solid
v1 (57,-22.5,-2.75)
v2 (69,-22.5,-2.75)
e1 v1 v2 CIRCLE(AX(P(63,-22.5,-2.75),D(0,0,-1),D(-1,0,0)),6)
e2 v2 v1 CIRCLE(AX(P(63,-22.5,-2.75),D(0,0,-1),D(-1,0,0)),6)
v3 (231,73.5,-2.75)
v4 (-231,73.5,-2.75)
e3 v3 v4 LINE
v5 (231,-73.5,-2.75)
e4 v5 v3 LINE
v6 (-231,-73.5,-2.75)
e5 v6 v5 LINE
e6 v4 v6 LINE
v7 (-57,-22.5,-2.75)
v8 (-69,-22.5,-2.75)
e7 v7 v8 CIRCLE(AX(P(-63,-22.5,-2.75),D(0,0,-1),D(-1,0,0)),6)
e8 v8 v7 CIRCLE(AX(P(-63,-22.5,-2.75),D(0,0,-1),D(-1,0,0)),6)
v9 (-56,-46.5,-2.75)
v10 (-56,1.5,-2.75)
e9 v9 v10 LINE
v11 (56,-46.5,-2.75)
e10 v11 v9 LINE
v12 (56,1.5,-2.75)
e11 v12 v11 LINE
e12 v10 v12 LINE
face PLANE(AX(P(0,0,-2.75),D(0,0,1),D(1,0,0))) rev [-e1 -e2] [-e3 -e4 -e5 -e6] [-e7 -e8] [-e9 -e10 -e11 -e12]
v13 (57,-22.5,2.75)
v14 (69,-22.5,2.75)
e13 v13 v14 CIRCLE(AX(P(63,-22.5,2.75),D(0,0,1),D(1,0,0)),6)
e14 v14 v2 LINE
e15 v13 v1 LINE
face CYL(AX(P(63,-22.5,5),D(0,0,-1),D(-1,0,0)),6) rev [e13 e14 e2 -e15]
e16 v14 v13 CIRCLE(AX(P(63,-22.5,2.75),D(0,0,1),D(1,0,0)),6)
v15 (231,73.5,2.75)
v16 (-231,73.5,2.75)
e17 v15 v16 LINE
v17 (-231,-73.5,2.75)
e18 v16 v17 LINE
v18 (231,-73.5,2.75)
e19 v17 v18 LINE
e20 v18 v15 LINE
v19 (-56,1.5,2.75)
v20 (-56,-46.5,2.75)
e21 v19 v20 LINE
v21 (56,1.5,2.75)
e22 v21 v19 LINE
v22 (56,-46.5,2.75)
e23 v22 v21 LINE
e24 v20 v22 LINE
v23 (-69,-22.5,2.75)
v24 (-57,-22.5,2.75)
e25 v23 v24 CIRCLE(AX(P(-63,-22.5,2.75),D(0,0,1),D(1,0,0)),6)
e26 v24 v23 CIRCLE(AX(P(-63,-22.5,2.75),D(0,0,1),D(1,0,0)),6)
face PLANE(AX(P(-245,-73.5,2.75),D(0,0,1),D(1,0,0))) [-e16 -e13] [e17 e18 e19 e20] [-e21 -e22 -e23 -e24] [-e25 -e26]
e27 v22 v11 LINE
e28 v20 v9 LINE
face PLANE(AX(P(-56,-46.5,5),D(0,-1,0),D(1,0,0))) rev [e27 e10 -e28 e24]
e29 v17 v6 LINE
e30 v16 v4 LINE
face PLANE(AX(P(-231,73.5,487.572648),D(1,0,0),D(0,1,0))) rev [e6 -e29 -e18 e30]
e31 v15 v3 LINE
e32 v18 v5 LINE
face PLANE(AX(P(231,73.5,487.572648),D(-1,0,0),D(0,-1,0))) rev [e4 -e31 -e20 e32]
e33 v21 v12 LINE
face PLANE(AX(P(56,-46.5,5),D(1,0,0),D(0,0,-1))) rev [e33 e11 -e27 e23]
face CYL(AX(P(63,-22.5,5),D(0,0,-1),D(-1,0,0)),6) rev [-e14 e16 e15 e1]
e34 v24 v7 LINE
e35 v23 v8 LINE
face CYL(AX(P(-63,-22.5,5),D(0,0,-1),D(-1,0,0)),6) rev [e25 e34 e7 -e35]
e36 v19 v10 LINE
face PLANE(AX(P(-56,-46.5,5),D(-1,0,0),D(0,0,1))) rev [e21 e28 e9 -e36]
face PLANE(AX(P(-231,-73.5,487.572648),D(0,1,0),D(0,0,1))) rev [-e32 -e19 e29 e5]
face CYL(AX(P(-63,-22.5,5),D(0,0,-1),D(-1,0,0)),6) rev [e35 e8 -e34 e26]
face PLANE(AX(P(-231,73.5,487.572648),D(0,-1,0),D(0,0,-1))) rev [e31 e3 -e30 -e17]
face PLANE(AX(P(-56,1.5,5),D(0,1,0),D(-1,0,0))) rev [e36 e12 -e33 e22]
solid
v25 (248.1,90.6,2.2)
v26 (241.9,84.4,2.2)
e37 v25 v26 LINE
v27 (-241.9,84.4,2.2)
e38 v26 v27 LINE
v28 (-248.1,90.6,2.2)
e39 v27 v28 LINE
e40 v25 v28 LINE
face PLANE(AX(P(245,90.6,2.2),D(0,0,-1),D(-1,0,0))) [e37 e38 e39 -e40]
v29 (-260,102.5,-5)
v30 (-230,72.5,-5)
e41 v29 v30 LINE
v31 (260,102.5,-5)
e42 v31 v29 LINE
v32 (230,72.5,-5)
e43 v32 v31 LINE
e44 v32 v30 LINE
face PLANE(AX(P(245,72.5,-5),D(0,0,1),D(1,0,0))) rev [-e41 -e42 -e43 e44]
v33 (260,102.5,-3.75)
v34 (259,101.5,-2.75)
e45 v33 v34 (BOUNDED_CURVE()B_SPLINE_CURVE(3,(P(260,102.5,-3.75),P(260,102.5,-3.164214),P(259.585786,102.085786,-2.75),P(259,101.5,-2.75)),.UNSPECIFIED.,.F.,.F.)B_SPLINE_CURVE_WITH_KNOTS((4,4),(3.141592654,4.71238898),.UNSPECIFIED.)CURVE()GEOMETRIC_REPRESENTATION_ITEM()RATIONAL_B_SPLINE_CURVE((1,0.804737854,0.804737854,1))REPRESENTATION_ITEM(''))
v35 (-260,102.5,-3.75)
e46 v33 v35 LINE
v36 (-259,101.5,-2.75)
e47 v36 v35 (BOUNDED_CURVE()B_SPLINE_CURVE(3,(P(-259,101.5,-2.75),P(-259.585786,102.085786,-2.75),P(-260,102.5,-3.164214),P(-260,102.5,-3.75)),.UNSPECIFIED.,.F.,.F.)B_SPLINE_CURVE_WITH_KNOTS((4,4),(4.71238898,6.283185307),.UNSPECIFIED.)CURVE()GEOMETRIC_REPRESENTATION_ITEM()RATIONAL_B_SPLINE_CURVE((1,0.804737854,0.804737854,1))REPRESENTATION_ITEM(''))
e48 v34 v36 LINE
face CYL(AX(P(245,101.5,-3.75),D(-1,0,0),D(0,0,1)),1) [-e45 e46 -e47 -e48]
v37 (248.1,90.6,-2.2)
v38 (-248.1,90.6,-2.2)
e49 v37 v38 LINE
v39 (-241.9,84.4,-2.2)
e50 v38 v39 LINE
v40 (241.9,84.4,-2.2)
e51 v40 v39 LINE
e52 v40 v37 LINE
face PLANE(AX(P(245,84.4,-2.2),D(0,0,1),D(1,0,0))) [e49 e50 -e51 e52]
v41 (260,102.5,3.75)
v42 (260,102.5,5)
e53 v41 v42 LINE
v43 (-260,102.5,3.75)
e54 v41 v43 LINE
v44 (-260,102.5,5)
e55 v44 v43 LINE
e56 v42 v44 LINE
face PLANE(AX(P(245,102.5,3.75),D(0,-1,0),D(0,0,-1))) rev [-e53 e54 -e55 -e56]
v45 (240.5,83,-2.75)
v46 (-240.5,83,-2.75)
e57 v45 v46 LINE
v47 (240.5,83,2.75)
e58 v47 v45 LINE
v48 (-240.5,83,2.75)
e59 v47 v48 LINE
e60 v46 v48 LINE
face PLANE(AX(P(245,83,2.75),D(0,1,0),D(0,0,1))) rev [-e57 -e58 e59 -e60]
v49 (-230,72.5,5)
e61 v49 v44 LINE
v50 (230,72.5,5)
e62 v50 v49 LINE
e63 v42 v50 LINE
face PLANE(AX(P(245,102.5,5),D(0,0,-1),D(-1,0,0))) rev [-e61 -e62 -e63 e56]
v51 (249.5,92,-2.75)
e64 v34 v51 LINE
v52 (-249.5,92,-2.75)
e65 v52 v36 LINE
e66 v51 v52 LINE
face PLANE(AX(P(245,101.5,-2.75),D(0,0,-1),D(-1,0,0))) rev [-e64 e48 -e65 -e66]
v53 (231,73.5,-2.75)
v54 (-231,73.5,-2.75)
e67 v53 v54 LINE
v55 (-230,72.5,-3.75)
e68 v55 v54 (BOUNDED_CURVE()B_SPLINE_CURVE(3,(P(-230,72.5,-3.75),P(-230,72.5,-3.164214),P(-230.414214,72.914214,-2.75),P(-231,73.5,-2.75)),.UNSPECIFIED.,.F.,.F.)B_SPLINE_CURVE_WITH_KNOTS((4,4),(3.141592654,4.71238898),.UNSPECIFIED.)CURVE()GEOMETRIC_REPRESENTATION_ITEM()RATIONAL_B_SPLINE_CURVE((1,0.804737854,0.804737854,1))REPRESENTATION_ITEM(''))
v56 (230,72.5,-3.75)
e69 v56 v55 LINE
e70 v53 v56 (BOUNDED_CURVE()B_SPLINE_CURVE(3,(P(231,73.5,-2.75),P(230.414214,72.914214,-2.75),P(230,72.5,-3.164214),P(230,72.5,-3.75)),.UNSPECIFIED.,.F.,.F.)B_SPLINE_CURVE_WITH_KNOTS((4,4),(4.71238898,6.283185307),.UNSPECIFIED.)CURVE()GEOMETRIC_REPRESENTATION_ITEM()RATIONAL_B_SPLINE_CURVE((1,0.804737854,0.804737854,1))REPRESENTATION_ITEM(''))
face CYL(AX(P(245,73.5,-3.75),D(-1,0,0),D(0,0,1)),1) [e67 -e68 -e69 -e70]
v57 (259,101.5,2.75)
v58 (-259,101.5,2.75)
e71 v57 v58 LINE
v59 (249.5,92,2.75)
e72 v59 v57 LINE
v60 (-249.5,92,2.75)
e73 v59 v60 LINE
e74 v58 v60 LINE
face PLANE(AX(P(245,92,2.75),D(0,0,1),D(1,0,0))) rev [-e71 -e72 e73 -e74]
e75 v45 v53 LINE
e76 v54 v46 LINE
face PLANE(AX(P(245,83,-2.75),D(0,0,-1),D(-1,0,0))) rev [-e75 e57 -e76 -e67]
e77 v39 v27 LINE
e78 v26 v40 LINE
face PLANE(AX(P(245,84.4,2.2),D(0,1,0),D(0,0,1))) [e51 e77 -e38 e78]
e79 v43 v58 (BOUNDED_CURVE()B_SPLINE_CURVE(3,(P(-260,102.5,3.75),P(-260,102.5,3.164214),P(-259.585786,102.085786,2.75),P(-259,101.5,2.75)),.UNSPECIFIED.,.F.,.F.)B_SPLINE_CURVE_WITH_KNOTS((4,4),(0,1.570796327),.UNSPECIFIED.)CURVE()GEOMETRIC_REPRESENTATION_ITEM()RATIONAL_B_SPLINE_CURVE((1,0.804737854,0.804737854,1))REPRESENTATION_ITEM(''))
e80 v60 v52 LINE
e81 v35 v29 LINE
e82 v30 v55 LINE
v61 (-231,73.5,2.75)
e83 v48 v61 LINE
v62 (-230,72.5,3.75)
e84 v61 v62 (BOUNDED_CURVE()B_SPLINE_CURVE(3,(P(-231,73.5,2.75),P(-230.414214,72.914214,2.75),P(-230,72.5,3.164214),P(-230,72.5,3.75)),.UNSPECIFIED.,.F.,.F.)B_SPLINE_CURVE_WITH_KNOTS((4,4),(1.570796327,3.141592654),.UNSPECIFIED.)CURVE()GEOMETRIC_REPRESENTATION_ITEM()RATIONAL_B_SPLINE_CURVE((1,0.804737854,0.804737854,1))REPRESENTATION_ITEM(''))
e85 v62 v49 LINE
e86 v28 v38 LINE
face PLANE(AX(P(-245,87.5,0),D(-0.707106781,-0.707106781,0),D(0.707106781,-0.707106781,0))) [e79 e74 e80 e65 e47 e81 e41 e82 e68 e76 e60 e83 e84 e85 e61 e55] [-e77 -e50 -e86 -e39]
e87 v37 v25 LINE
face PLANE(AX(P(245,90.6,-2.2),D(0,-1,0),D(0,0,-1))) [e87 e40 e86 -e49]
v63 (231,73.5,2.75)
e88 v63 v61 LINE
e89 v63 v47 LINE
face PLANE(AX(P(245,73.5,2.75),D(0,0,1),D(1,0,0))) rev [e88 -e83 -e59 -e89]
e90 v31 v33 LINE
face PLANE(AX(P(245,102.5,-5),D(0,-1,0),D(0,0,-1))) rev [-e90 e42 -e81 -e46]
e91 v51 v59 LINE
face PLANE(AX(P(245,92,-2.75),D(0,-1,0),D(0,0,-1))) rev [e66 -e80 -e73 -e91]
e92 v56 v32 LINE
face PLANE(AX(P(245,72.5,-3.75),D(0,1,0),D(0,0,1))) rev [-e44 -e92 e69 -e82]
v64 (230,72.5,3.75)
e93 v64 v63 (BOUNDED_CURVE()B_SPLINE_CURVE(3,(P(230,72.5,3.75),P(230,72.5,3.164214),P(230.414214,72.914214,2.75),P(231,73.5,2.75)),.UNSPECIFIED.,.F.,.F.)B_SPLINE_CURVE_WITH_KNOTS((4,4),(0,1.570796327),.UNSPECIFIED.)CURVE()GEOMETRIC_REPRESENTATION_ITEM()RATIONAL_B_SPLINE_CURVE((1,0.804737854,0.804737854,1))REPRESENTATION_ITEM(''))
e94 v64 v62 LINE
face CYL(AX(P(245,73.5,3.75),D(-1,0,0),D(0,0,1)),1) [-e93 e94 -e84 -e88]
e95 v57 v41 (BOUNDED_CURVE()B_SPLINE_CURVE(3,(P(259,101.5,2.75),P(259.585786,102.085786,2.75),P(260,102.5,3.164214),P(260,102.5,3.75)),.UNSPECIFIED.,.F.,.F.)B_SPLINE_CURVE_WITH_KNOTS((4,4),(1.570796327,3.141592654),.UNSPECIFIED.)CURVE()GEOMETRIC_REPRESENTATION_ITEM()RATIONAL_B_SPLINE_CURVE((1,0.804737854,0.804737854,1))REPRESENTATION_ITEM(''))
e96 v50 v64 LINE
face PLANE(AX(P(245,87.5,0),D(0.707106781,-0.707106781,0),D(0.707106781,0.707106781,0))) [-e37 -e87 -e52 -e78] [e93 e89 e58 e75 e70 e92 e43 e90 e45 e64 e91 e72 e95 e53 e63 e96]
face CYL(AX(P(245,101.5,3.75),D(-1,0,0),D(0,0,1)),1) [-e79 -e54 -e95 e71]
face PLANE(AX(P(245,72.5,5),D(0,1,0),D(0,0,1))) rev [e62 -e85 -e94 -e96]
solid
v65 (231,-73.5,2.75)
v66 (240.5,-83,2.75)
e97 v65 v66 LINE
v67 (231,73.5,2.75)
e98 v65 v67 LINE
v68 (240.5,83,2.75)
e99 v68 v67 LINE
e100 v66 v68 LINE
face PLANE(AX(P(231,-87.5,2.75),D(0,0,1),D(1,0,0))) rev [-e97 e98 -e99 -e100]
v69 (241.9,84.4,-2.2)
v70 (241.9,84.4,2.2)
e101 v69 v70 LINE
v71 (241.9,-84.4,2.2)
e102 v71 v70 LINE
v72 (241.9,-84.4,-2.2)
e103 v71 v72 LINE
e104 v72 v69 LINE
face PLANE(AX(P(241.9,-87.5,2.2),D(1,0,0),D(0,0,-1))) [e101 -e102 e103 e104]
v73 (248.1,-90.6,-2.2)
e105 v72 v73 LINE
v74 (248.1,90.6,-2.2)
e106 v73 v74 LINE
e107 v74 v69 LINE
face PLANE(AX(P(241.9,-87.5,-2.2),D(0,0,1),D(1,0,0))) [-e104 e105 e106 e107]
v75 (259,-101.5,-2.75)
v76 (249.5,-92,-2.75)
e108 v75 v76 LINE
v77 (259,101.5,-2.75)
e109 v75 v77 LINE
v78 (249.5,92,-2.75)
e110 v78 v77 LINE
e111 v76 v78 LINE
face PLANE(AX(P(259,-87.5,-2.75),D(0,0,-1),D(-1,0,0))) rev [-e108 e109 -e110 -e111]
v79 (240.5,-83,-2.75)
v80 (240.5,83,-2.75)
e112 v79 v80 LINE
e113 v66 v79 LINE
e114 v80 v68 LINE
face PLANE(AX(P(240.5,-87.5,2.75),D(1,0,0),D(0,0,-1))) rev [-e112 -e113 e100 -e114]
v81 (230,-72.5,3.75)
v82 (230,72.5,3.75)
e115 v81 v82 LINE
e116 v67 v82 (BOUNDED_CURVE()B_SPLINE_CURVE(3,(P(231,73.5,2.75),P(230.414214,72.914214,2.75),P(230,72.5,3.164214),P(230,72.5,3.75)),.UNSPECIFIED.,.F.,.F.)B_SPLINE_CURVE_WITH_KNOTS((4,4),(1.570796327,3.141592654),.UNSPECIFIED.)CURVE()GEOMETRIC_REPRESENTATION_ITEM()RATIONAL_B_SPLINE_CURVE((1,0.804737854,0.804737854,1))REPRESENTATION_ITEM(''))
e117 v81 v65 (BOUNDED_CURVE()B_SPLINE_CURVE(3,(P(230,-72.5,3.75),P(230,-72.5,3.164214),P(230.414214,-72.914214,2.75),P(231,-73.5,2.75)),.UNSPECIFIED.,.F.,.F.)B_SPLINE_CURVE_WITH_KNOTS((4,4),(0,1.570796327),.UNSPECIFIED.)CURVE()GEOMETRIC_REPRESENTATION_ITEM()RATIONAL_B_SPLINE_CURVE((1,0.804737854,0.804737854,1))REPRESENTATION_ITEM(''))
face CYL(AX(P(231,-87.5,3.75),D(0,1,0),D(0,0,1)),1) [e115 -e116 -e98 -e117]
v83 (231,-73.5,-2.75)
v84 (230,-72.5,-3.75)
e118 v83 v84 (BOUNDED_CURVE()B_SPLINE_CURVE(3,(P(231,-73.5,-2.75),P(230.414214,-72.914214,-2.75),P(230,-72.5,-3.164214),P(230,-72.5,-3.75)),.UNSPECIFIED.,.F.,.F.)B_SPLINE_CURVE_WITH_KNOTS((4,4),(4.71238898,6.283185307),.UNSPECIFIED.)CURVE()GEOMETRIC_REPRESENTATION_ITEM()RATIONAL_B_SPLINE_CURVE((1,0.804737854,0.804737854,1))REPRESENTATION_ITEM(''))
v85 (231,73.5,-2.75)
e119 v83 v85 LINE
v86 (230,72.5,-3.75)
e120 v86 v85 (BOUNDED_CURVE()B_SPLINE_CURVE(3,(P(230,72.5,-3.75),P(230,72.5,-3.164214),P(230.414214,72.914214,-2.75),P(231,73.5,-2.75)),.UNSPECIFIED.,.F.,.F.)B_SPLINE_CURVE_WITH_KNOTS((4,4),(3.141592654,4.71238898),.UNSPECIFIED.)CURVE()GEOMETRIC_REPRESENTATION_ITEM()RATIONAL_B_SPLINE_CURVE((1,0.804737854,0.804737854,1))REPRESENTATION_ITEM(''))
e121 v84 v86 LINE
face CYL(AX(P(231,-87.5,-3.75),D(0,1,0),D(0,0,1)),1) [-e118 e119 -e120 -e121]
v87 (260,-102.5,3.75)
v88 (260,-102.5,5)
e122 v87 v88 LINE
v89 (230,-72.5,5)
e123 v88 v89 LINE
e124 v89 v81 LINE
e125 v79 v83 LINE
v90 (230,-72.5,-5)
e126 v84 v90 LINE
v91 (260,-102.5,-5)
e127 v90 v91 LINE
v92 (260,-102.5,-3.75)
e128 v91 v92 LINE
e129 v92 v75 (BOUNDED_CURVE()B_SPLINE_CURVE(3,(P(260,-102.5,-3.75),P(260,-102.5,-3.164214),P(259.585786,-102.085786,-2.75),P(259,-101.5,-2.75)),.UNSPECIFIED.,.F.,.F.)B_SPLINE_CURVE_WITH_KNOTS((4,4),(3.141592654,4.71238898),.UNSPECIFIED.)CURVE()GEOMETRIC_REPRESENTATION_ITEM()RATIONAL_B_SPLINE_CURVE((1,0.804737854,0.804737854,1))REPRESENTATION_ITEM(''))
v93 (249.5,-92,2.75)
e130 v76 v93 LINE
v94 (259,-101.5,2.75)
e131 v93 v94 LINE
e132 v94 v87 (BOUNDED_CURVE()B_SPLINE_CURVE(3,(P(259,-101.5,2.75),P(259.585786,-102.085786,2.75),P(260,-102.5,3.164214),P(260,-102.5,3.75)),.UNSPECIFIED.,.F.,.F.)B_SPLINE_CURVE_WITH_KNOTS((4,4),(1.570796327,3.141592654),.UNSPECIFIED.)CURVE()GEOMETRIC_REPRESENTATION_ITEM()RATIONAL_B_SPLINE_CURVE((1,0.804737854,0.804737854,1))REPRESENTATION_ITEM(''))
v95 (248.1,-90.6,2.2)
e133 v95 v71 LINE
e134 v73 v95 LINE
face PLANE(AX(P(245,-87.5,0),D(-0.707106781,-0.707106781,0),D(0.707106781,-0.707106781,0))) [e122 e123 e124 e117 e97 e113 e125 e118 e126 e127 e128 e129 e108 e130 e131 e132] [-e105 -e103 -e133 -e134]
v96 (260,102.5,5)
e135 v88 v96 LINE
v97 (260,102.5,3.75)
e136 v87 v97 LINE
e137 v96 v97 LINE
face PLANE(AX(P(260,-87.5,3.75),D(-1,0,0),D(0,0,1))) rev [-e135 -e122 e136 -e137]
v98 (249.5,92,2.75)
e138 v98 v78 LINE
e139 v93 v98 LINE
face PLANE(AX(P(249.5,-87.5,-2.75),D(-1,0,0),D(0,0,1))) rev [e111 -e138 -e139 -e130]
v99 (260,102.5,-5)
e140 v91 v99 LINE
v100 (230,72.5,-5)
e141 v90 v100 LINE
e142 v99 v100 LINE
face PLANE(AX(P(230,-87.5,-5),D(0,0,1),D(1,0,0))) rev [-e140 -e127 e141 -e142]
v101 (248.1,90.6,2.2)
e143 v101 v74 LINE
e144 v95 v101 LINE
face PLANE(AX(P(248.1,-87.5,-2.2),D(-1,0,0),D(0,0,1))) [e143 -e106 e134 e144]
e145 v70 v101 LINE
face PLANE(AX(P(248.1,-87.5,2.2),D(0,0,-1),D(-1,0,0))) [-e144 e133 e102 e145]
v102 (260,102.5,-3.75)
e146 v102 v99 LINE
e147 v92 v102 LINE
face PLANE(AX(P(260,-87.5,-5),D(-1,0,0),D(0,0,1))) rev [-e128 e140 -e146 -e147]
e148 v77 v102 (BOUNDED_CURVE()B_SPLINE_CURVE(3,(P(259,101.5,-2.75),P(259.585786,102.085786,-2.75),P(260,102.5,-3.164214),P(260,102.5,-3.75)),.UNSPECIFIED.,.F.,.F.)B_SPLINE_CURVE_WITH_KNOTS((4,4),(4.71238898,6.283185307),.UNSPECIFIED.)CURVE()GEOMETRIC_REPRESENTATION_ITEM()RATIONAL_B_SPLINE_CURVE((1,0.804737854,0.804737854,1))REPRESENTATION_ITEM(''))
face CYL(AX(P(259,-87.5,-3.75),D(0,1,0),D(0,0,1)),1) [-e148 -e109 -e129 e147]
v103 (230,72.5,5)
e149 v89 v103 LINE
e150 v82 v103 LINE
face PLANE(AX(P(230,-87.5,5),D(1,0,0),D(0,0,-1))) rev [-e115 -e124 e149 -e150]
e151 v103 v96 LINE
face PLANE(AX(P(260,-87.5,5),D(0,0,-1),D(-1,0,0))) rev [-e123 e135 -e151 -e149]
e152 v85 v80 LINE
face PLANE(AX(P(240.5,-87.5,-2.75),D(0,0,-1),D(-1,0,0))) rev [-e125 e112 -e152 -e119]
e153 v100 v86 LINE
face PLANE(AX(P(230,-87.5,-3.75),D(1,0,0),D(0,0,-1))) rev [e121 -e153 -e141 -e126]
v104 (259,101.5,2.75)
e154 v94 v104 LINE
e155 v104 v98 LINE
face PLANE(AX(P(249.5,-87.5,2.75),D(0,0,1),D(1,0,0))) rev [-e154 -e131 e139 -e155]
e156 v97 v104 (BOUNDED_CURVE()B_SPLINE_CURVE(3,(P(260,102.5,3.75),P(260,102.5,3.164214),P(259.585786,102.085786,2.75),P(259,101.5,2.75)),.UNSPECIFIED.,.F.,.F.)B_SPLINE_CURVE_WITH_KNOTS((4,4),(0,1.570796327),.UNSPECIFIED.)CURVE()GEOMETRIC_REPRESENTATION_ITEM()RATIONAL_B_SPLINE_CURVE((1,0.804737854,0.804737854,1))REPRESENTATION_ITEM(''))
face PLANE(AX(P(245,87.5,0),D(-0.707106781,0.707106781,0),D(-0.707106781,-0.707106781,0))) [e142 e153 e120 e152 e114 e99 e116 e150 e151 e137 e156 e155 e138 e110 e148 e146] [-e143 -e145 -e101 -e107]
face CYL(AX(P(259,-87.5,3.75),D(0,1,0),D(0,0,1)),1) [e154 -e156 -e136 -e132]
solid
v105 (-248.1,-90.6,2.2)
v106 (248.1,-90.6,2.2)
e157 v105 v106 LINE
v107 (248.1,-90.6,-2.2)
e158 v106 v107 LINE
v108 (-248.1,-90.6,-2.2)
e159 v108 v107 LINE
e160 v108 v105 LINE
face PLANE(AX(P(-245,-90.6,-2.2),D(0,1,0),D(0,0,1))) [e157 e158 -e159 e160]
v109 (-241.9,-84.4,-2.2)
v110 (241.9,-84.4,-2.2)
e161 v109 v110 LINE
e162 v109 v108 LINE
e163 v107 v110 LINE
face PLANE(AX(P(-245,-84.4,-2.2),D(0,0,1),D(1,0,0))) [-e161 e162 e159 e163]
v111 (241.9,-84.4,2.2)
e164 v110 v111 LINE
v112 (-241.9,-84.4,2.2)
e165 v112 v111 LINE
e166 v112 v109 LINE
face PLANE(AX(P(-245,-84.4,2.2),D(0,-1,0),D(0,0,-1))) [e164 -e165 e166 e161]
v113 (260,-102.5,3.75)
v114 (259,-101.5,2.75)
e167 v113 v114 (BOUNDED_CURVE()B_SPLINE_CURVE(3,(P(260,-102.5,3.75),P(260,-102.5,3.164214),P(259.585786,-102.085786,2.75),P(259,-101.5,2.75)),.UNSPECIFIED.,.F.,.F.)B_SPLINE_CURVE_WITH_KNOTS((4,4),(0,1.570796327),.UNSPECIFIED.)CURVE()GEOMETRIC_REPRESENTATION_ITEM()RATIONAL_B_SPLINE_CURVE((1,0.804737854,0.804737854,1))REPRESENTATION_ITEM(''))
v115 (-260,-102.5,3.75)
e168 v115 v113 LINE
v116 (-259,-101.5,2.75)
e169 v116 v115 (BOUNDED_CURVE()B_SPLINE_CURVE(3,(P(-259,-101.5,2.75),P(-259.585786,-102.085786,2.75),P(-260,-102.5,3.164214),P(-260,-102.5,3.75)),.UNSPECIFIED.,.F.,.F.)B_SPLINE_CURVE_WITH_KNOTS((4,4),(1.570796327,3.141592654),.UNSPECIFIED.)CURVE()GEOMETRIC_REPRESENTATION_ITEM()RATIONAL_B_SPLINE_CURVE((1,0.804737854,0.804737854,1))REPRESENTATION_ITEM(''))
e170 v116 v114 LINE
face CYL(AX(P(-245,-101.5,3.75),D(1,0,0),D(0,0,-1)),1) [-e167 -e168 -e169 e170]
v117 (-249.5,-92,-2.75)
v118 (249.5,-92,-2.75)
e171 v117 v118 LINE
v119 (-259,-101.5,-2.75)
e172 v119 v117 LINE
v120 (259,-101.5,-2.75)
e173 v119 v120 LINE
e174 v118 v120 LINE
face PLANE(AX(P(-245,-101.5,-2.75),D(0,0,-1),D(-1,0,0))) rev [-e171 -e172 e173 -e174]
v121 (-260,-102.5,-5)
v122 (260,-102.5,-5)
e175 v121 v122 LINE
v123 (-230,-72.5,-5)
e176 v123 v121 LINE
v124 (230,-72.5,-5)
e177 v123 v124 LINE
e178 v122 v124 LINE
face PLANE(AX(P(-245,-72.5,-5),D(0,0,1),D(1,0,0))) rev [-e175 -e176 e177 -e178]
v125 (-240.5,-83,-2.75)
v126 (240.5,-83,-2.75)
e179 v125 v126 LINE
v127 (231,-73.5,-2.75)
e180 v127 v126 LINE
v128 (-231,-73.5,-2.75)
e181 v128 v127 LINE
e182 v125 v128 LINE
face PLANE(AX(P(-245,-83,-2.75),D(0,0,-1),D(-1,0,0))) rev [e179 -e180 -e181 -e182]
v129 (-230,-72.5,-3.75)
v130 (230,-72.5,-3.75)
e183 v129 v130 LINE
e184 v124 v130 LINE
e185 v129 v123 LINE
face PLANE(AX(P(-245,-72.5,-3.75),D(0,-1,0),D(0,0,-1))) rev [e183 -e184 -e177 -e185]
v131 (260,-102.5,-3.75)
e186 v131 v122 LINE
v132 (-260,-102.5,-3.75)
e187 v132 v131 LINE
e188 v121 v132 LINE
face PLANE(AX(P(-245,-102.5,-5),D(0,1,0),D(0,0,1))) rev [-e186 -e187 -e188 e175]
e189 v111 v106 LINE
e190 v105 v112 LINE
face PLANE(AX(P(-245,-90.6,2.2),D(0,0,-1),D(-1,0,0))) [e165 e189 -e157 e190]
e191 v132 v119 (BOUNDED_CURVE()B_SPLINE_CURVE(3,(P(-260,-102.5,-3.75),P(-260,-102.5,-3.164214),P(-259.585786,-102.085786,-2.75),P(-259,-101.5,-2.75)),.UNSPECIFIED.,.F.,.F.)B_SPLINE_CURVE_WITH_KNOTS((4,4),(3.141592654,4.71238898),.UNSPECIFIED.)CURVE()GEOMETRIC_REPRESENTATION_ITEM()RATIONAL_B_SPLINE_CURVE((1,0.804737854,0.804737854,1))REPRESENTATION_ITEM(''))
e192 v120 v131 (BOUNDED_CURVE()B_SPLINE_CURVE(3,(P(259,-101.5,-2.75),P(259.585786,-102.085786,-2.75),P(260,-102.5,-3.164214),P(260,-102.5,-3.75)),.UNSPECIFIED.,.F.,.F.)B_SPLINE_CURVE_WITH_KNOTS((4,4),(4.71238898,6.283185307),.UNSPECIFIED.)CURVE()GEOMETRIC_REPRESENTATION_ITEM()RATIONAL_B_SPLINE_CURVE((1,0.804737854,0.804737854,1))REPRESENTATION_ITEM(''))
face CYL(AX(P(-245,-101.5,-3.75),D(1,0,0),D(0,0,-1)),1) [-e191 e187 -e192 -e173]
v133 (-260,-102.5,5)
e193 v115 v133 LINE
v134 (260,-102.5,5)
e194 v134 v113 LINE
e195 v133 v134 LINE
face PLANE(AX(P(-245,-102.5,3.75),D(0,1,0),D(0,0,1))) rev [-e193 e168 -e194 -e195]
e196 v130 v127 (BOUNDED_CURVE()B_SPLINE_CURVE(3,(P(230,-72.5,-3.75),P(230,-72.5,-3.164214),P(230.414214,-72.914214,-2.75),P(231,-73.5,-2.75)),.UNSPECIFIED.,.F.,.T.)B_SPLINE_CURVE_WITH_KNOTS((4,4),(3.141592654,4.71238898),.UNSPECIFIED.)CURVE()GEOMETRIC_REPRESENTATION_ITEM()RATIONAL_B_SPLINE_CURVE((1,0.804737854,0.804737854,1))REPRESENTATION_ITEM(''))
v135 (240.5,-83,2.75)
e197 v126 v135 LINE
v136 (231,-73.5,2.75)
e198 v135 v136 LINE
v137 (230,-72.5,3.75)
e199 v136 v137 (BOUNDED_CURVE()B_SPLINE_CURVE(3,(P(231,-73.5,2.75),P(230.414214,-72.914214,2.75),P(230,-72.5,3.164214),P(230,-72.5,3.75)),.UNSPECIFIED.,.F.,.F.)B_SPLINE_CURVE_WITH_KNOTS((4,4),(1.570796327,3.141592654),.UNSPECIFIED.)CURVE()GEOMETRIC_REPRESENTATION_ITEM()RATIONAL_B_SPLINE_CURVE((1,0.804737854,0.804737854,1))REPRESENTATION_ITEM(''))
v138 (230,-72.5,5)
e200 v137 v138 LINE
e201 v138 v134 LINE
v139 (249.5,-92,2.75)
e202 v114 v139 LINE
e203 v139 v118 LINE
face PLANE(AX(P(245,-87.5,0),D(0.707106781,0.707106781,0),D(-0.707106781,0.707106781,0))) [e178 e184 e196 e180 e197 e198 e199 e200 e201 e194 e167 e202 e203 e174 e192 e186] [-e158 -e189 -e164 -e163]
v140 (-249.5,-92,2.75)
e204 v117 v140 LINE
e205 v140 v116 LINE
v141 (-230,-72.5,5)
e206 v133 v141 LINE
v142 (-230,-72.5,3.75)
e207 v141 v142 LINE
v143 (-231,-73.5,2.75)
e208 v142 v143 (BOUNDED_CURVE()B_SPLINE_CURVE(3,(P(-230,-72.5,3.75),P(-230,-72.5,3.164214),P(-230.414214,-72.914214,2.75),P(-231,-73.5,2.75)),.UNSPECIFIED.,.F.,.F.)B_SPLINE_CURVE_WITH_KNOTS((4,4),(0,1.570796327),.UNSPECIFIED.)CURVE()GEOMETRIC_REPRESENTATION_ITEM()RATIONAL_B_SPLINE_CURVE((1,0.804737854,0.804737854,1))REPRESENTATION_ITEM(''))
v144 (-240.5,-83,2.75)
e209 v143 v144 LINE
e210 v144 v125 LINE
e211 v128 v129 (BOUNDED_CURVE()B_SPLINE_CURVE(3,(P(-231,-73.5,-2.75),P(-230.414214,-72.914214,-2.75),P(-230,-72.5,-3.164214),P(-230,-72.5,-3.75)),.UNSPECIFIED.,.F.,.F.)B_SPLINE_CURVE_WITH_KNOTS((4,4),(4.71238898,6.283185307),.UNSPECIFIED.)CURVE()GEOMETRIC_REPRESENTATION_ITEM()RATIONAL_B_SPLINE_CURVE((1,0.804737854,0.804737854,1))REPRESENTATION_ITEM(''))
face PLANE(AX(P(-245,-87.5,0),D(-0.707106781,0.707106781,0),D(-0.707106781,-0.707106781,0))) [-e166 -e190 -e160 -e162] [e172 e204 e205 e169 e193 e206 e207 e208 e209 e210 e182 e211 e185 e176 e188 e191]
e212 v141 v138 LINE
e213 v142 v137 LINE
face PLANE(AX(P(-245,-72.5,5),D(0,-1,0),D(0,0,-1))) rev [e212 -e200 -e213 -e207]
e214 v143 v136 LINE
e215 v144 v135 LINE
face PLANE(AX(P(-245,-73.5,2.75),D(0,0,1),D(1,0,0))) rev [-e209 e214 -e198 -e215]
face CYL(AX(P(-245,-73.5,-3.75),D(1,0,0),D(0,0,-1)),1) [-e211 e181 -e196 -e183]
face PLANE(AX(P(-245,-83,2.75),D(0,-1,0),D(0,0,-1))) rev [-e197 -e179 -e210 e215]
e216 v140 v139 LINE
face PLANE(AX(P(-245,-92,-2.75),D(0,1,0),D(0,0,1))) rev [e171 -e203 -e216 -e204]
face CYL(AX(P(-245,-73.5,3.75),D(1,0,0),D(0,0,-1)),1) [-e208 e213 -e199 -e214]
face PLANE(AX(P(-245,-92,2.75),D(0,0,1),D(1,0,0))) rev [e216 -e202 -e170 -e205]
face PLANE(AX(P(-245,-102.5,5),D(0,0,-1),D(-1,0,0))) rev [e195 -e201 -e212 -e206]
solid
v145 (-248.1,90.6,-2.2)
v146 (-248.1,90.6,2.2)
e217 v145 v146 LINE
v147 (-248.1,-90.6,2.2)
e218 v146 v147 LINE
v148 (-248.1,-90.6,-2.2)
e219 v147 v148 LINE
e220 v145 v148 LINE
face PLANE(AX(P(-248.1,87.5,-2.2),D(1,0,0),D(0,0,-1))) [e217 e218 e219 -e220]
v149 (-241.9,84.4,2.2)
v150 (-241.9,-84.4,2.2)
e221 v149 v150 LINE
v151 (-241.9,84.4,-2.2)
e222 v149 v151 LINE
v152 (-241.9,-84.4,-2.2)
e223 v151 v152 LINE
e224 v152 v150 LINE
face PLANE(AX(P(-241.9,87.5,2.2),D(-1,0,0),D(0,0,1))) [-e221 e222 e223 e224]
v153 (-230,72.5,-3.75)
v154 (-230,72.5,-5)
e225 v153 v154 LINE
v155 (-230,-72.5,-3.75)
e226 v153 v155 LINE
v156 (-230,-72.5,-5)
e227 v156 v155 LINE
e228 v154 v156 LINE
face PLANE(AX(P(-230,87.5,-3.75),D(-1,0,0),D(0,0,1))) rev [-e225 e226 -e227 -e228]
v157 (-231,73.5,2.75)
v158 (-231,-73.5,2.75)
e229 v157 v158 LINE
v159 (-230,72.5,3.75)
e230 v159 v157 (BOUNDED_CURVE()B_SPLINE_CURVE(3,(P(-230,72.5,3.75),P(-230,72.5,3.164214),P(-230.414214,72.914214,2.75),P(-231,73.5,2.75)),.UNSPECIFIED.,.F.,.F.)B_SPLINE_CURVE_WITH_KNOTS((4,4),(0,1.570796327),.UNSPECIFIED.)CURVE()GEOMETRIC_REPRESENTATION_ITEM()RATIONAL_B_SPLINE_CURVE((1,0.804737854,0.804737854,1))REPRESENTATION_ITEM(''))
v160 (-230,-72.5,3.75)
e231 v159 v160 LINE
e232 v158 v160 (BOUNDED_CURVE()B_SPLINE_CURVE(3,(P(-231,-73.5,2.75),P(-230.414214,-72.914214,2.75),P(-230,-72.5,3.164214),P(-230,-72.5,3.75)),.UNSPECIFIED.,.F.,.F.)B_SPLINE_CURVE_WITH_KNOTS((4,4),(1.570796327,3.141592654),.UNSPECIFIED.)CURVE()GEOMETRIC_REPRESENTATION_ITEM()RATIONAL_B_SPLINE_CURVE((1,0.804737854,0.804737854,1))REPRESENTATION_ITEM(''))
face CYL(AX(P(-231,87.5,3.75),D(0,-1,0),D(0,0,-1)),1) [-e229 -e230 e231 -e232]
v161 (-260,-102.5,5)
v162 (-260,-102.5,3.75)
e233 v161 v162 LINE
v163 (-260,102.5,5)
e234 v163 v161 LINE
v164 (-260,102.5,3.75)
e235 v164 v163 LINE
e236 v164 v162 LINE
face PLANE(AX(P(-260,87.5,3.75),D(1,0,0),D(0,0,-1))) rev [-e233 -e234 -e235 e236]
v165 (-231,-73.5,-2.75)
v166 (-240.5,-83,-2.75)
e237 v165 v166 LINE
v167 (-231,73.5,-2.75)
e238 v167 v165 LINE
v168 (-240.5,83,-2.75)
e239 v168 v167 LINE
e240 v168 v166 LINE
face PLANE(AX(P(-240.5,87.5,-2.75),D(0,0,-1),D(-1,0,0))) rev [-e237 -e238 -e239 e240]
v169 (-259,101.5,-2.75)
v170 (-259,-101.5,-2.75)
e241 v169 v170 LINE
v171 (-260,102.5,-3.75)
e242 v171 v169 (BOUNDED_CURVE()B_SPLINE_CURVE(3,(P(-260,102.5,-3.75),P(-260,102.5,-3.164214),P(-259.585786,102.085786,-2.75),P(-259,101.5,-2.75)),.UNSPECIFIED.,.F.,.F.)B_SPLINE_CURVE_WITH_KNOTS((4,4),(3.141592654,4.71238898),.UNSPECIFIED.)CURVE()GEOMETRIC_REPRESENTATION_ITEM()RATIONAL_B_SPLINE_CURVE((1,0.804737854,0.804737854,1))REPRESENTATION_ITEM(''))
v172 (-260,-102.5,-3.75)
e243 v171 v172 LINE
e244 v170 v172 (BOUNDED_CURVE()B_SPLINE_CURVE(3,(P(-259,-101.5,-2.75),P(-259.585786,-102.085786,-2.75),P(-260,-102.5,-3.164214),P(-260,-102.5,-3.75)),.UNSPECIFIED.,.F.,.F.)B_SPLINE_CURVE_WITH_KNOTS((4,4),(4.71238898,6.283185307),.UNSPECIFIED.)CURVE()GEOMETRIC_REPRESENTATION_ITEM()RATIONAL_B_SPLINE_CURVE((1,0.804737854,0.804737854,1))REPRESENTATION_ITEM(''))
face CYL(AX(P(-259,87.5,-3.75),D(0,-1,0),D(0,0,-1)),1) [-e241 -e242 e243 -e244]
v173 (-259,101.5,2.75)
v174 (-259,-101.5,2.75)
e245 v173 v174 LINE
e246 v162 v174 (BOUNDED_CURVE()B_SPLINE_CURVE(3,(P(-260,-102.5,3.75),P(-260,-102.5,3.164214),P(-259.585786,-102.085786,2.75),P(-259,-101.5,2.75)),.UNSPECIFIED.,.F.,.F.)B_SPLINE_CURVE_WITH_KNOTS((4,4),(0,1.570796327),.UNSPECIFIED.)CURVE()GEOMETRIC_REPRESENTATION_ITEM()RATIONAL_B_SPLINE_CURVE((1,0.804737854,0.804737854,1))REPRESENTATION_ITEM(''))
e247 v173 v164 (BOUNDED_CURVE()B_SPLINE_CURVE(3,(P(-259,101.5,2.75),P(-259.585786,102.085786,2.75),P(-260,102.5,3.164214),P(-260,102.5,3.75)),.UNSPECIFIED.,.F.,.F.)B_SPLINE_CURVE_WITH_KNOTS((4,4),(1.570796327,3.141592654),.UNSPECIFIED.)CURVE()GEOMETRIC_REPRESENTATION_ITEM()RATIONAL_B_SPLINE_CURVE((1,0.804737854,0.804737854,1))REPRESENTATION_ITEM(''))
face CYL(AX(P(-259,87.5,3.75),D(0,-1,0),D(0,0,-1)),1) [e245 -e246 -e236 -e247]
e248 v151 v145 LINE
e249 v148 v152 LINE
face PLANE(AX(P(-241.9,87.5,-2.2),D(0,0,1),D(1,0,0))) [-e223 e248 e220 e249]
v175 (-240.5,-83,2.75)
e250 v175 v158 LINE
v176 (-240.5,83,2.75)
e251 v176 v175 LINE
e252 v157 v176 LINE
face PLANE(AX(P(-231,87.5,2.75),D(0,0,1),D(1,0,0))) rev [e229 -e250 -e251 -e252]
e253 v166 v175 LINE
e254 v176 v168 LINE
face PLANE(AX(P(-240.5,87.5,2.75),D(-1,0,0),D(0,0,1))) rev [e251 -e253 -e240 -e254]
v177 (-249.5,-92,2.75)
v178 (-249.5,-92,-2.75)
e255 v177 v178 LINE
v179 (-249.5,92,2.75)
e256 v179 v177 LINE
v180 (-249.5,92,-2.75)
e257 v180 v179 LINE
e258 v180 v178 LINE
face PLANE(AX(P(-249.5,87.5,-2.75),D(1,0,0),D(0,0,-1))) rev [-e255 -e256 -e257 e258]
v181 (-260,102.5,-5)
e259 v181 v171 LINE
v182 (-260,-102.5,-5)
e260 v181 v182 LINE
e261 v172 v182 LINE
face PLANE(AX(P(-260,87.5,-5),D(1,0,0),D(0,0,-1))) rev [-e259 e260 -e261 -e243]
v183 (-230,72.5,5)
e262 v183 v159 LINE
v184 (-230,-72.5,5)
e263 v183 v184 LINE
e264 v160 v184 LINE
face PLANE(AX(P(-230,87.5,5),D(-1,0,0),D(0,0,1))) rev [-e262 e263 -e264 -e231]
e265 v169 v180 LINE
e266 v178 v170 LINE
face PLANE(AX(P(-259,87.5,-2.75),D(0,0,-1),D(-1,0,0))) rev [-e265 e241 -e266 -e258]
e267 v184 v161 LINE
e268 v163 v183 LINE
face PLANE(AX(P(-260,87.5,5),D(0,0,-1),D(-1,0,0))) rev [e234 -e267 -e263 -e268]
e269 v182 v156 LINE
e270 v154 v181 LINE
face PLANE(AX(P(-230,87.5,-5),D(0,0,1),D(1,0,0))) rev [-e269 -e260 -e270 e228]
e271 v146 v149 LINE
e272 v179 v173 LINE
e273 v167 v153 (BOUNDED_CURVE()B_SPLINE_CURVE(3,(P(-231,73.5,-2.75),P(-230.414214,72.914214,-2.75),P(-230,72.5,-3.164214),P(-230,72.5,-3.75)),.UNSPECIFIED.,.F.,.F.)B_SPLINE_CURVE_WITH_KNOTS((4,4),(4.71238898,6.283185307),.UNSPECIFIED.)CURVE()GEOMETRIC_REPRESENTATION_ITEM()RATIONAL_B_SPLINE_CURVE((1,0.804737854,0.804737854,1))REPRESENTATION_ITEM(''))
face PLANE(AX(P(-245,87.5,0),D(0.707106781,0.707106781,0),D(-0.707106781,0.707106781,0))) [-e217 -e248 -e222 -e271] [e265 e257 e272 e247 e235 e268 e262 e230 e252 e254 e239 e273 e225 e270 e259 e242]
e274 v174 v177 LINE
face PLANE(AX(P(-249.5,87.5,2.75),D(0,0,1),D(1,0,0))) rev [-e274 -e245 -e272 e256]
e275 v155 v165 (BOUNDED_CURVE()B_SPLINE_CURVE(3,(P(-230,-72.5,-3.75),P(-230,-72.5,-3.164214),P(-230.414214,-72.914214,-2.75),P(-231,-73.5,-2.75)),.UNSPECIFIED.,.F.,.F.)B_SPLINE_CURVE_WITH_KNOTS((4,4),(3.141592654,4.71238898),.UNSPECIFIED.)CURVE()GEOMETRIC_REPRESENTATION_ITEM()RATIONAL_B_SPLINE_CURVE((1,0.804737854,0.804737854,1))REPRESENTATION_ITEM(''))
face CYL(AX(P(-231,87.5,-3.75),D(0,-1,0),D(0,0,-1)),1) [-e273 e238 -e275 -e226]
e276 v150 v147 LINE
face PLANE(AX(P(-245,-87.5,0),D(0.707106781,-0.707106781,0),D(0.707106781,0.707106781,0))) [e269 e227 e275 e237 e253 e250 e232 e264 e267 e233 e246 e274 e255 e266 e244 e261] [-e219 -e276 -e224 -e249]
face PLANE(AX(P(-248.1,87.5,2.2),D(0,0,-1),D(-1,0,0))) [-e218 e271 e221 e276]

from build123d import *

# Parameters (mm, degrees)
ALUMINIUM_PROFILE_20_X_20_X_2_1_DEPTH      = 506.811388301
ALUMINIUM_PROFILE_20_X_20_X_2_1_DEPTH_BACK = 16.811388301
SKETCH1_W                                  = 6.2
SKETCH1_H                                  = 4.4
SKETCH1_ON_SEGMENT_2_W                     = 6.2
SKETCH1_ON_SEGMENT_2_H                     = 4.4
ALUMINIUM_PROFILE_20_X_20_X_2_1_2_DEPTH    = 208.622776602
SKETCH1_ON_SEGMENT_3_W                     = 6.2
SKETCH1_ON_SEGMENT_3_H                     = 4.4
ALUMINIUM_PROFILE_20_X_20_X_2_1_3_DEPTH    = 523.622776602
SKETCH1_ON_SEGMENT_4_W                     = 6.2
SKETCH1_ON_SEGMENT_4_H                     = 4.4
ALUMINIUM_PROFILE_20_X_20_X_2_1_4_DEPTH    = 208.622776602
SKETCH3_W                                  = 462
SKETCH3_H                                  = 147
BOSS_EXTRUDE1_DEPTH                        = 5.5
SKETCH4_R                                  = 6
SKETCH4_W                                  = 112
SKETCH4_H                                  = 48
CUT_EXTRUDE1_DEPTH                         = 280.582389467


with BuildPart() as part:
    # Sketch1 → Aluminium profile 20 X 20 X 2(1) (new, two sides: drawn at the far end of the back side and taken through both)
    with BuildSketch(Plane(origin=(-245, 87.5, 0), x_dir=(0, 1, 0), z_dir=(1, 0, 0)).offset(-ALUMINIUM_PROFILE_20_X_20_X_2_1_DEPTH_BACK)):
        with BuildLine():
            Line((4.5, 2.75), (14, 2.75))
            ThreePointArc((14, 2.75), (14.707106781, 3.042893219), (15, 3.75))
            Line((15, 3.75), (15, 5))
            Line((15, 5), (-15, 5))
            Line((-15, 5), (-15, 3.75))
            ThreePointArc((-15, 3.75), (-14.707106781, 3.042893219), (-14, 2.75))
            Line((-14, 2.75), (-4.5, 2.75))
            Line((-4.5, 2.75), (-4.5, -2.75))
            Line((-4.5, -2.75), (-14, -2.75))
            ThreePointArc((-14, -2.75), (-14.707106781, -3.042893219), (-15, -3.75))
            Line((-15, -3.75), (-15, -5))
            Line((-15, -5), (15, -5))
            Line((15, -5), (15, -3.75))
            ThreePointArc((15, -3.75), (14.707106781, -3.042893219), (14, -2.75))
            Line((14, -2.75), (4.5, -2.75))
            Line((4.5, -2.75), (4.5, 2.75))
        make_face()
        Rectangle(SKETCH1_W, SKETCH1_H, mode=Mode.SUBTRACT)
    extrude(amount=ALUMINIUM_PROFILE_20_X_20_X_2_1_DEPTH + ALUMINIUM_PROFILE_20_X_20_X_2_1_DEPTH_BACK)

    # Aluminium profile 20 X 20 X 2(1) mitre 1
    split(bisect_by=Plane(origin=(-245, 87.5, 0), x_dir=(-0.707106781, 0.707106781, 0), z_dir=(0.707106781, 0.707106781, 0)), keep=Keep.TOP)

    # Aluminium profile 20 X 20 X 2(1) mitre 2
    split(bisect_by=Plane(origin=(245, 87.5, 0), x_dir=(-0.707106781, -0.707106781, 0), z_dir=(-0.707106781, 0.707106781, 0)), keep=Keep.TOP)


with BuildPart() as body_2:
    # Sketch1 on segment 2 (carried to segment 2) → Aluminium profile 20 X 20 X 2_1 2 (new body)
    with BuildSketch(Plane(origin=(245, 104.311388301, 0), x_dir=(1, 0, 0), z_dir=(0, -1, 0))):
        with BuildLine():
            Line((4.5, 2.75), (14, 2.75))
            ThreePointArc((14, 2.75), (14.707106781, 3.042893219), (15, 3.75))
            Line((15, 3.75), (15, 5))
            Line((15, 5), (-15, 5))
            Line((-15, 5), (-15, 3.75))
            ThreePointArc((-15, 3.75), (-14.707106781, 3.042893219), (-14, 2.75))
            Line((-14, 2.75), (-4.5, 2.75))
            Line((-4.5, 2.75), (-4.5, -2.75))
            Line((-4.5, -2.75), (-14, -2.75))
            ThreePointArc((-14, -2.75), (-14.707106781, -3.042893219), (-15, -3.75))
            Line((-15, -3.75), (-15, -5))
            Line((-15, -5), (15, -5))
            Line((15, -5), (15, -3.75))
            ThreePointArc((15, -3.75), (14.707106781, -3.042893219), (14, -2.75))
            Line((14, -2.75), (4.5, -2.75))
            Line((4.5, -2.75), (4.5, 2.75))
        make_face()
        Rectangle(SKETCH1_ON_SEGMENT_2_W, SKETCH1_ON_SEGMENT_2_H, mode=Mode.SUBTRACT)
    extrude(amount=ALUMINIUM_PROFILE_20_X_20_X_2_1_2_DEPTH)

    # Aluminium profile 20 X 20 X 2_1 2 mitre
    split(bisect_by=Plane(origin=(245, -87.5, 0), x_dir=(-0.707106781, 0.707106781, 0), z_dir=(0.707106781, 0.707106781, 0)), keep=Keep.TOP)

    # Aluminium profile 20 X 20 X 2_1 2 mi 2
    split(bisect_by=Plane(origin=(245, 87.5, 0), x_dir=(0.707106781, 0.707106781, 0), z_dir=(0.707106781, -0.707106781, 0)), keep=Keep.TOP)


with BuildPart() as body_3:
    # Sketch1 on segment 3 (carried to segment 3) → Aluminium profile 20 X 20 X 2_1 3 (new body)
    with BuildSketch(Plane(origin=(261.811388301, -87.5, 0), x_dir=(0, -1, 0), z_dir=(-1, 0, 0))):
        with BuildLine():
            Line((4.5, 2.75), (14, 2.75))
            ThreePointArc((14, 2.75), (14.707106781, 3.042893219), (15, 3.75))
            Line((15, 3.75), (15, 5))
            Line((15, 5), (-15, 5))
            Line((-15, 5), (-15, 3.75))
            ThreePointArc((-15, 3.75), (-14.707106781, 3.042893219), (-14, 2.75))
            Line((-14, 2.75), (-4.5, 2.75))
            Line((-4.5, 2.75), (-4.5, -2.75))
            Line((-4.5, -2.75), (-14, -2.75))
            ThreePointArc((-14, -2.75), (-14.707106781, -3.042893219), (-15, -3.75))
            Line((-15, -3.75), (-15, -5))
            Line((-15, -5), (15, -5))
            Line((15, -5), (15, -3.75))
            ThreePointArc((15, -3.75), (14.707106781, -3.042893219), (14, -2.75))
            Line((14, -2.75), (4.5, -2.75))
            Line((4.5, -2.75), (4.5, 2.75))
        make_face()
        Rectangle(SKETCH1_ON_SEGMENT_3_W, SKETCH1_ON_SEGMENT_3_H, mode=Mode.SUBTRACT)
    extrude(amount=ALUMINIUM_PROFILE_20_X_20_X_2_1_3_DEPTH)

    # Aluminium profile 20 X 20 X 2_1 3 mitre
    split(bisect_by=Plane(origin=(-245, -87.5, 0), x_dir=(0.707106781, 0.707106781, 0), z_dir=(0.707106781, -0.707106781, 0)), keep=Keep.TOP)

    # Aluminium profile 20 X 20 X 2_1 3 mi 2
    split(bisect_by=Plane(origin=(245, -87.5, 0), x_dir=(0.707106781, -0.707106781, 0), z_dir=(-0.707106781, -0.707106781, 0)), keep=Keep.TOP)


with BuildPart() as body_4:
    # Sketch1 on segment 4 (carried to segment 4) → Aluminium profile 20 X 20 X 2_1 4 (new body)
    with BuildSketch(Plane(origin=(-245, -104.311388301, 0), x_dir=(-1, 0, 0), z_dir=(0, 1, 0))):
        with BuildLine():
            Line((4.5, 2.75), (14, 2.75))
            ThreePointArc((14, 2.75), (14.707106781, 3.042893219), (15, 3.75))
            Line((15, 3.75), (15, 5))
            Line((15, 5), (-15, 5))
            Line((-15, 5), (-15, 3.75))
            ThreePointArc((-15, 3.75), (-14.707106781, 3.042893219), (-14, 2.75))
            Line((-14, 2.75), (-4.5, 2.75))
            Line((-4.5, 2.75), (-4.5, -2.75))
            Line((-4.5, -2.75), (-14, -2.75))
            ThreePointArc((-14, -2.75), (-14.707106781, -3.042893219), (-15, -3.75))
            Line((-15, -3.75), (-15, -5))
            Line((-15, -5), (15, -5))
            Line((15, -5), (15, -3.75))
            ThreePointArc((15, -3.75), (14.707106781, -3.042893219), (14, -2.75))
            Line((14, -2.75), (4.5, -2.75))
            Line((4.5, -2.75), (4.5, 2.75))
        make_face()
        Rectangle(SKETCH1_ON_SEGMENT_4_W, SKETCH1_ON_SEGMENT_4_H, mode=Mode.SUBTRACT)
    extrude(amount=ALUMINIUM_PROFILE_20_X_20_X_2_1_4_DEPTH)

    # Aluminium profile 20 X 20 X 2_1 4 mitre
    split(bisect_by=Plane(origin=(-245, -87.5, 0), x_dir=(-0.707106781, -0.707106781, 0), z_dir=(-0.707106781, 0.707106781, 0)), keep=Keep.TOP)

    # Aluminium profile 20 X 20 X 2_1 4 mi 2
    split(bisect_by=Plane(origin=(-245, 87.5, 0), x_dir=(0.707106781, -0.707106781, 0), z_dir=(-0.707106781, -0.707106781, 0)), keep=Keep.TOP)


with BuildPart() as body_5:
    # Sketch3 → Boss-Extrude1 (new body)
    with BuildSketch(Plane.XY.offset(-2.75)):
        Rectangle(SKETCH3_W, SKETCH3_H)
    extrude(amount=BOSS_EXTRUDE1_DEPTH)

    # Sketch4 → Cut-Extrude1 (cut, through all)
    with BuildSketch(Plane(origin=(0, 0, -2.75), x_dir=(-1, 0, 0), z_dir=(0, 0, -1))):
        with Locations((-63, -22.5)):
            Circle(SKETCH4_R)
        with Locations((63, -22.5)):
            Circle(SKETCH4_R)
        with Locations((0, -22.5)):
            Rectangle(SKETCH4_W, SKETCH4_H)
    extrude(amount=-CUT_EXTRUDE1_DEPTH, mode=Mode.SUBTRACT)


solid = Compound([part.part, body_2.part, body_3.part, body_4.part, body_5.part])
